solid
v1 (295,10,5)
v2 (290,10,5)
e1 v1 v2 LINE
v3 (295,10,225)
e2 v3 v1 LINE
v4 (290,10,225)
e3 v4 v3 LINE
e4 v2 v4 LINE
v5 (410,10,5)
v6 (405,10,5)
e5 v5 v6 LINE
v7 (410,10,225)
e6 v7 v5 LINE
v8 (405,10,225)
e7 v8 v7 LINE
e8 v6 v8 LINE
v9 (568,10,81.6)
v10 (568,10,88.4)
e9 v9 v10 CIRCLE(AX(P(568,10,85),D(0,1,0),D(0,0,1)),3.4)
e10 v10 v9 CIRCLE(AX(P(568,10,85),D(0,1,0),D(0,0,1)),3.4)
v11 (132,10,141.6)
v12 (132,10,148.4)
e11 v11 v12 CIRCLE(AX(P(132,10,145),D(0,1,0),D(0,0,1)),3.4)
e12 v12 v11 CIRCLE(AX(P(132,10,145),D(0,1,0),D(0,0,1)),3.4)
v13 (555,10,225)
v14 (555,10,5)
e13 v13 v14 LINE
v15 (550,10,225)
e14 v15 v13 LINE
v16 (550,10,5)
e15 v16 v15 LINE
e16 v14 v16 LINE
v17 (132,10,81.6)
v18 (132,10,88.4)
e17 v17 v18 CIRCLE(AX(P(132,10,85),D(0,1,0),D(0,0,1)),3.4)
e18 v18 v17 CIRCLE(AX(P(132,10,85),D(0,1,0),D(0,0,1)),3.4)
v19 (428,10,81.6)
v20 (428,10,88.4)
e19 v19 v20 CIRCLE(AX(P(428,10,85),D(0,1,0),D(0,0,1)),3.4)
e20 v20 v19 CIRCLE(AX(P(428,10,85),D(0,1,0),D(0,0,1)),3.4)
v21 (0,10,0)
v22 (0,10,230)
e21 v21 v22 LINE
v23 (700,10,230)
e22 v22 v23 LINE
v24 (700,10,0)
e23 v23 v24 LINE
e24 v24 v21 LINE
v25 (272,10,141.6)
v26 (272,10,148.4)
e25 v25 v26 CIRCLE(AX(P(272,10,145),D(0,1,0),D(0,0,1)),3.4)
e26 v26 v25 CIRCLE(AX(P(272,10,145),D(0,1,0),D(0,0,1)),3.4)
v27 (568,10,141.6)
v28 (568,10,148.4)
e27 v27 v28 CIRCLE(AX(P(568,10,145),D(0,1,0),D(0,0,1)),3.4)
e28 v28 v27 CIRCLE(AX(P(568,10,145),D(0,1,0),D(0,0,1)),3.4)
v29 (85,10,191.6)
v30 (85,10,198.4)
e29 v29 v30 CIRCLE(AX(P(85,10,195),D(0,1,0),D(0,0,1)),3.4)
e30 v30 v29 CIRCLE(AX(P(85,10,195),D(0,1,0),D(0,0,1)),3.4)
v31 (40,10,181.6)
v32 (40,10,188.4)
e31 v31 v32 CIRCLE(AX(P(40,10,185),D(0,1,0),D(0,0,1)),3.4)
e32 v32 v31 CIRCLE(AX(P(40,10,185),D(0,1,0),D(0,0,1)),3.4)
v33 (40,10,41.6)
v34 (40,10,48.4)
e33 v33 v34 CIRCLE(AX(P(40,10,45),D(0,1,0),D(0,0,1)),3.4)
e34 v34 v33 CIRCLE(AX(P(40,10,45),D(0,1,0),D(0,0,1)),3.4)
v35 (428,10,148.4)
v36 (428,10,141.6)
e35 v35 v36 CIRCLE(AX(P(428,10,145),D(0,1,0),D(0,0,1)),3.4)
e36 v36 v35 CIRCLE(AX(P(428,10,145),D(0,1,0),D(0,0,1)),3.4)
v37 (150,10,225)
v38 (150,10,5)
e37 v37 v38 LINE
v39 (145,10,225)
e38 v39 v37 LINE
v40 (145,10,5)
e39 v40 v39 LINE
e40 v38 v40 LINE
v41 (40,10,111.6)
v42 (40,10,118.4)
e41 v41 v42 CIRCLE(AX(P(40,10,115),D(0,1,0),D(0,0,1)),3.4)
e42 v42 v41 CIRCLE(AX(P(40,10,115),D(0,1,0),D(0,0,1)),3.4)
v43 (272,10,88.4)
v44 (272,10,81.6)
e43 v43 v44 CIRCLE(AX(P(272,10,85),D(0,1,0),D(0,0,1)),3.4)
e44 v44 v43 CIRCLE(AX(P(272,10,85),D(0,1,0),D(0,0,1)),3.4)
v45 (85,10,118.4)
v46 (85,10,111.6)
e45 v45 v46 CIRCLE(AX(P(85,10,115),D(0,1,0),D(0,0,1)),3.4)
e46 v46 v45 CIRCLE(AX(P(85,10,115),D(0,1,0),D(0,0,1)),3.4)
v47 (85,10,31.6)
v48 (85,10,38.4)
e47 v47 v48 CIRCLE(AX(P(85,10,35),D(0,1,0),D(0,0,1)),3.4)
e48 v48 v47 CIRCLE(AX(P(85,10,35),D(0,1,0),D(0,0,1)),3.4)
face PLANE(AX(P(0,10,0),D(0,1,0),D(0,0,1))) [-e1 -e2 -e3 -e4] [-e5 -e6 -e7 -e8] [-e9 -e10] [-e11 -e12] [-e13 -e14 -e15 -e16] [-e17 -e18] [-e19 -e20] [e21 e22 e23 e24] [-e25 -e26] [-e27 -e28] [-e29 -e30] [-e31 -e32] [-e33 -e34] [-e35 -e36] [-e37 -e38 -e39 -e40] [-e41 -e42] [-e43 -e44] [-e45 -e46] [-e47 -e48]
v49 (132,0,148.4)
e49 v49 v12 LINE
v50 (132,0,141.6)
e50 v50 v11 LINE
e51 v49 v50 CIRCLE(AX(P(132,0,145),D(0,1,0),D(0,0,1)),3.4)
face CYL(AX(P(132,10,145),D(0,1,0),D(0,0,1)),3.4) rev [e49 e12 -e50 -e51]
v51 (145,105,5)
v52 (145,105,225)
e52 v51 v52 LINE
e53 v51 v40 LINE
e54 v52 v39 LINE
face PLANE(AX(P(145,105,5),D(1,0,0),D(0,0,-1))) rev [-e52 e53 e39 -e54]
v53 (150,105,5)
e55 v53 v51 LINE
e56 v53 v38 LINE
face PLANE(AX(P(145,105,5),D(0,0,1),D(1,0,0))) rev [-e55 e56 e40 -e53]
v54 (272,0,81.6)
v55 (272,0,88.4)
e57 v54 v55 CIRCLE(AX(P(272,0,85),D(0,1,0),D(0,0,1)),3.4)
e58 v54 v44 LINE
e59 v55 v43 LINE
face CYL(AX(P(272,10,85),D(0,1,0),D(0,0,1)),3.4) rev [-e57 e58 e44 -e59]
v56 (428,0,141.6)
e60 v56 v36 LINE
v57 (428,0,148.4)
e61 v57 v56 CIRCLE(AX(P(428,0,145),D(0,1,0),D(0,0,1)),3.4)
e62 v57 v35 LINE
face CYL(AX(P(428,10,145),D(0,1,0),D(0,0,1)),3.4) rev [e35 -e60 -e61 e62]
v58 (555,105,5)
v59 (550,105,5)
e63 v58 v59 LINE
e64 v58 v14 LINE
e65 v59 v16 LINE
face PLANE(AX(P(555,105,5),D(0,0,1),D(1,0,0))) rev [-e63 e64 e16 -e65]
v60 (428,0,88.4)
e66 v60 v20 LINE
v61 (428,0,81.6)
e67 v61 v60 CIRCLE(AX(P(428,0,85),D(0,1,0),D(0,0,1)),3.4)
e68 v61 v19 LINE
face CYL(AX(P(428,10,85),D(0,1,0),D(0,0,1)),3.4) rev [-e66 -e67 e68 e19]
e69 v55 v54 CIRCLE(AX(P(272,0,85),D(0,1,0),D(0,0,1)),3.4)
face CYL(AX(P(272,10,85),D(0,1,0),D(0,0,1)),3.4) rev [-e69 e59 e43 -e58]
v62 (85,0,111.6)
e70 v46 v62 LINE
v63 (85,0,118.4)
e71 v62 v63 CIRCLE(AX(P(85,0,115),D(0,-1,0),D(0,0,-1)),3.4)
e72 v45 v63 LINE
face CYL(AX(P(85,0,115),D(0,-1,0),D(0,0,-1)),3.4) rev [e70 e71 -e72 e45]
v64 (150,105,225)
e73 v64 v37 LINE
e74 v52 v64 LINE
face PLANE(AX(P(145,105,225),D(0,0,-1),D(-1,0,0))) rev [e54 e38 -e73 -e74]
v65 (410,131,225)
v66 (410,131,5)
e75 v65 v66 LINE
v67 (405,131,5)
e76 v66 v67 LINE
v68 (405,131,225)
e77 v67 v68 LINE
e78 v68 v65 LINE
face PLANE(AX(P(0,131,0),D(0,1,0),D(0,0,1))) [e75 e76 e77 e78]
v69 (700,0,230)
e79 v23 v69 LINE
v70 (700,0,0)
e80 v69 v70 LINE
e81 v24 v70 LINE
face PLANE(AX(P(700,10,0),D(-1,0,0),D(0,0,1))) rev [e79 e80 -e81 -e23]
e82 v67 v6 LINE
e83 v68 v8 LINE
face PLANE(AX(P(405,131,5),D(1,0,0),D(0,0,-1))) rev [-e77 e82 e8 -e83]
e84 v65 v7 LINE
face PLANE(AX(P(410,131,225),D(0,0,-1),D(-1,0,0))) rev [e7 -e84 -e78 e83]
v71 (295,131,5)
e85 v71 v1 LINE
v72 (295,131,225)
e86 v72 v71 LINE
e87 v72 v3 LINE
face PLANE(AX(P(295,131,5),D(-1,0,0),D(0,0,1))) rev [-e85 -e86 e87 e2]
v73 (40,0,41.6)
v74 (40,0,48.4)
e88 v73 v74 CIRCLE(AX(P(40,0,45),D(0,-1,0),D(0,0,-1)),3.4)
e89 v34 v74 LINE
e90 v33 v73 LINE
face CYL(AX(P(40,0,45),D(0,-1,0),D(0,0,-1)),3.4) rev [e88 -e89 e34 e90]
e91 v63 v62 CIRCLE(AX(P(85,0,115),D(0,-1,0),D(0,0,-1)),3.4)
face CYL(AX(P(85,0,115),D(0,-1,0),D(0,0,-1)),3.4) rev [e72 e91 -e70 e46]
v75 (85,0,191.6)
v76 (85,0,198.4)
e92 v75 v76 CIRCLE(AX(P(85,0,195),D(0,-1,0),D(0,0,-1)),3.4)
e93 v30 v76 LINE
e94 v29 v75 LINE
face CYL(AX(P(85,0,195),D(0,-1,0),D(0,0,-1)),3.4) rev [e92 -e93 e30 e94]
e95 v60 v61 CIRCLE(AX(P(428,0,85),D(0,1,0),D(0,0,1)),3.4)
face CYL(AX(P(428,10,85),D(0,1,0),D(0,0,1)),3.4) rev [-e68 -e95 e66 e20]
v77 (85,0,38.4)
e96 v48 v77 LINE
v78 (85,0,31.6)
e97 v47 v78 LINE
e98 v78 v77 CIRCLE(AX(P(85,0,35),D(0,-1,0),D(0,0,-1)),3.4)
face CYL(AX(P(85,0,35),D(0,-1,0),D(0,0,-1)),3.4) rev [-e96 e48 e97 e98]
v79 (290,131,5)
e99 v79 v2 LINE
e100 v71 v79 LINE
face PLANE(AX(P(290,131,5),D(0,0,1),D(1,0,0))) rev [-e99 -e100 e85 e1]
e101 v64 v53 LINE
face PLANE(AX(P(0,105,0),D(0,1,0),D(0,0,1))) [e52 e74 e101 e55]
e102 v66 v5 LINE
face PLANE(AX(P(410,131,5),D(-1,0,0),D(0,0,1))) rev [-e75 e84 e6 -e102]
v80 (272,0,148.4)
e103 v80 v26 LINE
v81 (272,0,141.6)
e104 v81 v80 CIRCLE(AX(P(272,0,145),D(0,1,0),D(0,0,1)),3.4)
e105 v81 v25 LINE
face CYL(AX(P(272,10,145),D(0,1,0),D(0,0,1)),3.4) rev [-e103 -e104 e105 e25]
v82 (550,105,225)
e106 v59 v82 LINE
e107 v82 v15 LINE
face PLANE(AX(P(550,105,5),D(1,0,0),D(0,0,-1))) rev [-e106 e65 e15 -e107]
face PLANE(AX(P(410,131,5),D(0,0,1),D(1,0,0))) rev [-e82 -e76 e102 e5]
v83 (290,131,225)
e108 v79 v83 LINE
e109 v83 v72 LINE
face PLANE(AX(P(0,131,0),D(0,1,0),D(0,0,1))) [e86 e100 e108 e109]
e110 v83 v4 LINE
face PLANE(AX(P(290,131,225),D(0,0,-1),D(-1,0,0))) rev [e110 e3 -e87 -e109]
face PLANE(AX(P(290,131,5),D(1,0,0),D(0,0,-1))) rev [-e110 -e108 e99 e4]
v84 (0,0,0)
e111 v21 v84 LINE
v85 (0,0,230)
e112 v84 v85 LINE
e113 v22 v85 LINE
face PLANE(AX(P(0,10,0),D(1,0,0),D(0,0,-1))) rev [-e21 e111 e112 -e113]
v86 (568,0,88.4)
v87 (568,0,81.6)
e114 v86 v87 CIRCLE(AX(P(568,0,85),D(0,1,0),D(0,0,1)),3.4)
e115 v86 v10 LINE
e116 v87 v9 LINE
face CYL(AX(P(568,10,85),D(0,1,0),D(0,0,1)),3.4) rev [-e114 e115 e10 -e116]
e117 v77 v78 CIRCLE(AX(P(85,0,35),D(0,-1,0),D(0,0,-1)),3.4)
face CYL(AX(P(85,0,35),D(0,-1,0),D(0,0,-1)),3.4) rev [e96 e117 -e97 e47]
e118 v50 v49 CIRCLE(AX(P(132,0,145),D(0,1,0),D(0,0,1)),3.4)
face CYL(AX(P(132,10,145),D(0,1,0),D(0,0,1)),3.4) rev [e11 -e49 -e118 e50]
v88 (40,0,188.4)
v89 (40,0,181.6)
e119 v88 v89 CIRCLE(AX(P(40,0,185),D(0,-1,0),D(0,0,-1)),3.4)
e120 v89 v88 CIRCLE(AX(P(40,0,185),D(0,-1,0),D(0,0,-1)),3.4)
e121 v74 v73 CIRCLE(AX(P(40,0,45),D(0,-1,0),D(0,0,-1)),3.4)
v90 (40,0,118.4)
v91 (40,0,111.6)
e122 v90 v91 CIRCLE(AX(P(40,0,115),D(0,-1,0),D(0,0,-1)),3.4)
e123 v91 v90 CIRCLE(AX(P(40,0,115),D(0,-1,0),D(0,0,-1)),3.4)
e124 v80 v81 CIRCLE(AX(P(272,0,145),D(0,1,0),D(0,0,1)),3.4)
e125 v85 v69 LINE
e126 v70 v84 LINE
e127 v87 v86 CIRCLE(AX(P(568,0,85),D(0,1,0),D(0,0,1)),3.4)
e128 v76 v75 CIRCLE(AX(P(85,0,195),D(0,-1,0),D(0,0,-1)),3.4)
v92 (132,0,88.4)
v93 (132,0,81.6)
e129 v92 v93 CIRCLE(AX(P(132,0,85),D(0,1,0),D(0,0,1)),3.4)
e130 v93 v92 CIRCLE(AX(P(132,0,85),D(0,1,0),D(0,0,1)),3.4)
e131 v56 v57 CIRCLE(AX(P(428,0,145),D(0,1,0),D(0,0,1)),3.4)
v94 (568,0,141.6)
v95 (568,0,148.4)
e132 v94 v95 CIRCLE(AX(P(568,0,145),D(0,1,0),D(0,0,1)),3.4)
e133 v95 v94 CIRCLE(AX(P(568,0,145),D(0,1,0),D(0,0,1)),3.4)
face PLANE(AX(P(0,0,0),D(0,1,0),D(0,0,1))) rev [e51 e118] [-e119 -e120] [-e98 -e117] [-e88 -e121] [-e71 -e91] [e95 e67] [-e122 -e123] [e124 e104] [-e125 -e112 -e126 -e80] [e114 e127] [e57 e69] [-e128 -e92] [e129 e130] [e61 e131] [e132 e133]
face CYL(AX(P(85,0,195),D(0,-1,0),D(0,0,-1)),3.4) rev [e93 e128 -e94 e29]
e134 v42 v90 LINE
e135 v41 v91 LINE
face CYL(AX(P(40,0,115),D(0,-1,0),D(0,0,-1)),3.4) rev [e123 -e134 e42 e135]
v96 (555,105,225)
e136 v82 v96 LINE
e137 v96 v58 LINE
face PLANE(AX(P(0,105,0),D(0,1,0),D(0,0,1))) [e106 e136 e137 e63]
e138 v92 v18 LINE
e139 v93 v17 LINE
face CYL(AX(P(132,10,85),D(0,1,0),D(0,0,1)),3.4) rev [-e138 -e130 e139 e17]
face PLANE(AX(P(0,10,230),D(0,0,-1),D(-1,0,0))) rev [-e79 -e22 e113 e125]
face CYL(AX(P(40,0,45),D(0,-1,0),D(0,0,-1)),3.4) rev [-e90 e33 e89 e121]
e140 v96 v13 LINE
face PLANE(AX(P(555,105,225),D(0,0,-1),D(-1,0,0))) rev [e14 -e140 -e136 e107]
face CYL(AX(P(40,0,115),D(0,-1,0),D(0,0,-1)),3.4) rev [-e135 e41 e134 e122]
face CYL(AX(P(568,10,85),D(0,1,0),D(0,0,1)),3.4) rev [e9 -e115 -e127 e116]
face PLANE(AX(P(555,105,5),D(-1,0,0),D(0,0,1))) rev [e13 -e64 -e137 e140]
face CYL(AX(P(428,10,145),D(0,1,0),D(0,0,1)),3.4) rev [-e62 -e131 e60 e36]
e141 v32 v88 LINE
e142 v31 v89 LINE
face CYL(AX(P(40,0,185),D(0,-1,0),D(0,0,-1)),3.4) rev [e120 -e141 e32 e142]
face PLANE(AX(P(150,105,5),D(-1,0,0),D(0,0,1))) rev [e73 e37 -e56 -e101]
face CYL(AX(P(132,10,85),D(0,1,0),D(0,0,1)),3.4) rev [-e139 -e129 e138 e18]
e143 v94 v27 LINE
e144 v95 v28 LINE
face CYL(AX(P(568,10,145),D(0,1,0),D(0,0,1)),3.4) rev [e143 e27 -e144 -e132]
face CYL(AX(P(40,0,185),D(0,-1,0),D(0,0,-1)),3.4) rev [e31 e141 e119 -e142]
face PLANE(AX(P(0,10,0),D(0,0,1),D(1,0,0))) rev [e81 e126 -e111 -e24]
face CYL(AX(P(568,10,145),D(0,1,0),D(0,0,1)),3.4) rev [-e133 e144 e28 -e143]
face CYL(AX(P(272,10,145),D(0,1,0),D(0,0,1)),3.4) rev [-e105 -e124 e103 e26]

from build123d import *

# Parameters (mm, degrees)
SKETCH1_W             = 700
SKETCH1_H             = 230
BOSS_EXTRUDE1_DEPTH   = 10
M8_TAPPED_HOLE1_D     = 6.8
SKETCH8_W             = 5
SKETCH8_H             = 220
BOSS_EXTRUDE2_DEPTH   = 121
SKETCH9_W             = 5
SKETCH9_H             = 220
BOSS_EXTRUDE3_DEPTH   = 95
M8_TAPPED_HOLE3_D     = 6.8
M8_TAPPED_HOLE3_DEPTH = 19.75
M8_TAPPED_HOLE3_TIP   = 2.042926105


with BuildPart() as part:
    # Sketch1 → Boss-Extrude1 (new body)
    with BuildSketch(Plane(origin=(0, 0, 0), x_dir=(1, 0, 0), z_dir=(0, 1, 0))):
        with Locations((350, -115)):
            Rectangle(SKETCH1_W, SKETCH1_H)
    extrude(amount=BOSS_EXTRUDE1_DEPTH)

    # M8 Tapped Hole1 (through all)
    with Locations(Plane(origin=(0, 10, 0), x_dir=(1, 0, 0), z_dir=(0, 1, 0))):
        with Locations((272, -85), (272, -145), (132, -145), (132, -85), (568, -85), (568, -145), (428, -145), (428, -85)):
            Hole(M8_TAPPED_HOLE1_D / 2)

    # Sketch8 → Boss-Extrude2 (add)
    with BuildSketch(Plane(origin=(0, 10, 0), x_dir=(1, 0, 0), z_dir=(0, 1, 0))):
        with Locations((292.5, -115)):
            Rectangle(SKETCH8_W, SKETCH8_H)
        with Locations((407.5, -115)):
            Rectangle(SKETCH8_W, SKETCH8_H)
    extrude(amount=BOSS_EXTRUDE2_DEPTH)

    # Sketch9 → Boss-Extrude3 (add)
    with BuildSketch(Plane(origin=(0, 10, 0), x_dir=(1, 0, 0), z_dir=(0, 1, 0))):
        with Locations((147.5, -115)):
            Rectangle(SKETCH9_W, SKETCH9_H)
        with Locations((552.5, -115)):
            Rectangle(SKETCH9_W, SKETCH9_H)
    extrude(amount=BOSS_EXTRUDE3_DEPTH)

    # M8 Tapped Hole3
    with Locations(Plane(origin=(0, 0, 0), x_dir=(-1, 0, 0), z_dir=(0, -1, 0))):
        with Locations((-85, -35), (-40, -45), (-40, -185), (-85, -195), (-40, -115), (-85, -115)):
            Hole(M8_TAPPED_HOLE3_D / 2, depth=M8_TAPPED_HOLE3_DEPTH)
            with Locations((0, 0, -(M8_TAPPED_HOLE3_DEPTH + M8_TAPPED_HOLE3_TIP / 2))):  # 118° drill point
                Cone(0, M8_TAPPED_HOLE3_D / 2, M8_TAPPED_HOLE3_TIP, mode=Mode.SUBTRACT)


solid = part.part
